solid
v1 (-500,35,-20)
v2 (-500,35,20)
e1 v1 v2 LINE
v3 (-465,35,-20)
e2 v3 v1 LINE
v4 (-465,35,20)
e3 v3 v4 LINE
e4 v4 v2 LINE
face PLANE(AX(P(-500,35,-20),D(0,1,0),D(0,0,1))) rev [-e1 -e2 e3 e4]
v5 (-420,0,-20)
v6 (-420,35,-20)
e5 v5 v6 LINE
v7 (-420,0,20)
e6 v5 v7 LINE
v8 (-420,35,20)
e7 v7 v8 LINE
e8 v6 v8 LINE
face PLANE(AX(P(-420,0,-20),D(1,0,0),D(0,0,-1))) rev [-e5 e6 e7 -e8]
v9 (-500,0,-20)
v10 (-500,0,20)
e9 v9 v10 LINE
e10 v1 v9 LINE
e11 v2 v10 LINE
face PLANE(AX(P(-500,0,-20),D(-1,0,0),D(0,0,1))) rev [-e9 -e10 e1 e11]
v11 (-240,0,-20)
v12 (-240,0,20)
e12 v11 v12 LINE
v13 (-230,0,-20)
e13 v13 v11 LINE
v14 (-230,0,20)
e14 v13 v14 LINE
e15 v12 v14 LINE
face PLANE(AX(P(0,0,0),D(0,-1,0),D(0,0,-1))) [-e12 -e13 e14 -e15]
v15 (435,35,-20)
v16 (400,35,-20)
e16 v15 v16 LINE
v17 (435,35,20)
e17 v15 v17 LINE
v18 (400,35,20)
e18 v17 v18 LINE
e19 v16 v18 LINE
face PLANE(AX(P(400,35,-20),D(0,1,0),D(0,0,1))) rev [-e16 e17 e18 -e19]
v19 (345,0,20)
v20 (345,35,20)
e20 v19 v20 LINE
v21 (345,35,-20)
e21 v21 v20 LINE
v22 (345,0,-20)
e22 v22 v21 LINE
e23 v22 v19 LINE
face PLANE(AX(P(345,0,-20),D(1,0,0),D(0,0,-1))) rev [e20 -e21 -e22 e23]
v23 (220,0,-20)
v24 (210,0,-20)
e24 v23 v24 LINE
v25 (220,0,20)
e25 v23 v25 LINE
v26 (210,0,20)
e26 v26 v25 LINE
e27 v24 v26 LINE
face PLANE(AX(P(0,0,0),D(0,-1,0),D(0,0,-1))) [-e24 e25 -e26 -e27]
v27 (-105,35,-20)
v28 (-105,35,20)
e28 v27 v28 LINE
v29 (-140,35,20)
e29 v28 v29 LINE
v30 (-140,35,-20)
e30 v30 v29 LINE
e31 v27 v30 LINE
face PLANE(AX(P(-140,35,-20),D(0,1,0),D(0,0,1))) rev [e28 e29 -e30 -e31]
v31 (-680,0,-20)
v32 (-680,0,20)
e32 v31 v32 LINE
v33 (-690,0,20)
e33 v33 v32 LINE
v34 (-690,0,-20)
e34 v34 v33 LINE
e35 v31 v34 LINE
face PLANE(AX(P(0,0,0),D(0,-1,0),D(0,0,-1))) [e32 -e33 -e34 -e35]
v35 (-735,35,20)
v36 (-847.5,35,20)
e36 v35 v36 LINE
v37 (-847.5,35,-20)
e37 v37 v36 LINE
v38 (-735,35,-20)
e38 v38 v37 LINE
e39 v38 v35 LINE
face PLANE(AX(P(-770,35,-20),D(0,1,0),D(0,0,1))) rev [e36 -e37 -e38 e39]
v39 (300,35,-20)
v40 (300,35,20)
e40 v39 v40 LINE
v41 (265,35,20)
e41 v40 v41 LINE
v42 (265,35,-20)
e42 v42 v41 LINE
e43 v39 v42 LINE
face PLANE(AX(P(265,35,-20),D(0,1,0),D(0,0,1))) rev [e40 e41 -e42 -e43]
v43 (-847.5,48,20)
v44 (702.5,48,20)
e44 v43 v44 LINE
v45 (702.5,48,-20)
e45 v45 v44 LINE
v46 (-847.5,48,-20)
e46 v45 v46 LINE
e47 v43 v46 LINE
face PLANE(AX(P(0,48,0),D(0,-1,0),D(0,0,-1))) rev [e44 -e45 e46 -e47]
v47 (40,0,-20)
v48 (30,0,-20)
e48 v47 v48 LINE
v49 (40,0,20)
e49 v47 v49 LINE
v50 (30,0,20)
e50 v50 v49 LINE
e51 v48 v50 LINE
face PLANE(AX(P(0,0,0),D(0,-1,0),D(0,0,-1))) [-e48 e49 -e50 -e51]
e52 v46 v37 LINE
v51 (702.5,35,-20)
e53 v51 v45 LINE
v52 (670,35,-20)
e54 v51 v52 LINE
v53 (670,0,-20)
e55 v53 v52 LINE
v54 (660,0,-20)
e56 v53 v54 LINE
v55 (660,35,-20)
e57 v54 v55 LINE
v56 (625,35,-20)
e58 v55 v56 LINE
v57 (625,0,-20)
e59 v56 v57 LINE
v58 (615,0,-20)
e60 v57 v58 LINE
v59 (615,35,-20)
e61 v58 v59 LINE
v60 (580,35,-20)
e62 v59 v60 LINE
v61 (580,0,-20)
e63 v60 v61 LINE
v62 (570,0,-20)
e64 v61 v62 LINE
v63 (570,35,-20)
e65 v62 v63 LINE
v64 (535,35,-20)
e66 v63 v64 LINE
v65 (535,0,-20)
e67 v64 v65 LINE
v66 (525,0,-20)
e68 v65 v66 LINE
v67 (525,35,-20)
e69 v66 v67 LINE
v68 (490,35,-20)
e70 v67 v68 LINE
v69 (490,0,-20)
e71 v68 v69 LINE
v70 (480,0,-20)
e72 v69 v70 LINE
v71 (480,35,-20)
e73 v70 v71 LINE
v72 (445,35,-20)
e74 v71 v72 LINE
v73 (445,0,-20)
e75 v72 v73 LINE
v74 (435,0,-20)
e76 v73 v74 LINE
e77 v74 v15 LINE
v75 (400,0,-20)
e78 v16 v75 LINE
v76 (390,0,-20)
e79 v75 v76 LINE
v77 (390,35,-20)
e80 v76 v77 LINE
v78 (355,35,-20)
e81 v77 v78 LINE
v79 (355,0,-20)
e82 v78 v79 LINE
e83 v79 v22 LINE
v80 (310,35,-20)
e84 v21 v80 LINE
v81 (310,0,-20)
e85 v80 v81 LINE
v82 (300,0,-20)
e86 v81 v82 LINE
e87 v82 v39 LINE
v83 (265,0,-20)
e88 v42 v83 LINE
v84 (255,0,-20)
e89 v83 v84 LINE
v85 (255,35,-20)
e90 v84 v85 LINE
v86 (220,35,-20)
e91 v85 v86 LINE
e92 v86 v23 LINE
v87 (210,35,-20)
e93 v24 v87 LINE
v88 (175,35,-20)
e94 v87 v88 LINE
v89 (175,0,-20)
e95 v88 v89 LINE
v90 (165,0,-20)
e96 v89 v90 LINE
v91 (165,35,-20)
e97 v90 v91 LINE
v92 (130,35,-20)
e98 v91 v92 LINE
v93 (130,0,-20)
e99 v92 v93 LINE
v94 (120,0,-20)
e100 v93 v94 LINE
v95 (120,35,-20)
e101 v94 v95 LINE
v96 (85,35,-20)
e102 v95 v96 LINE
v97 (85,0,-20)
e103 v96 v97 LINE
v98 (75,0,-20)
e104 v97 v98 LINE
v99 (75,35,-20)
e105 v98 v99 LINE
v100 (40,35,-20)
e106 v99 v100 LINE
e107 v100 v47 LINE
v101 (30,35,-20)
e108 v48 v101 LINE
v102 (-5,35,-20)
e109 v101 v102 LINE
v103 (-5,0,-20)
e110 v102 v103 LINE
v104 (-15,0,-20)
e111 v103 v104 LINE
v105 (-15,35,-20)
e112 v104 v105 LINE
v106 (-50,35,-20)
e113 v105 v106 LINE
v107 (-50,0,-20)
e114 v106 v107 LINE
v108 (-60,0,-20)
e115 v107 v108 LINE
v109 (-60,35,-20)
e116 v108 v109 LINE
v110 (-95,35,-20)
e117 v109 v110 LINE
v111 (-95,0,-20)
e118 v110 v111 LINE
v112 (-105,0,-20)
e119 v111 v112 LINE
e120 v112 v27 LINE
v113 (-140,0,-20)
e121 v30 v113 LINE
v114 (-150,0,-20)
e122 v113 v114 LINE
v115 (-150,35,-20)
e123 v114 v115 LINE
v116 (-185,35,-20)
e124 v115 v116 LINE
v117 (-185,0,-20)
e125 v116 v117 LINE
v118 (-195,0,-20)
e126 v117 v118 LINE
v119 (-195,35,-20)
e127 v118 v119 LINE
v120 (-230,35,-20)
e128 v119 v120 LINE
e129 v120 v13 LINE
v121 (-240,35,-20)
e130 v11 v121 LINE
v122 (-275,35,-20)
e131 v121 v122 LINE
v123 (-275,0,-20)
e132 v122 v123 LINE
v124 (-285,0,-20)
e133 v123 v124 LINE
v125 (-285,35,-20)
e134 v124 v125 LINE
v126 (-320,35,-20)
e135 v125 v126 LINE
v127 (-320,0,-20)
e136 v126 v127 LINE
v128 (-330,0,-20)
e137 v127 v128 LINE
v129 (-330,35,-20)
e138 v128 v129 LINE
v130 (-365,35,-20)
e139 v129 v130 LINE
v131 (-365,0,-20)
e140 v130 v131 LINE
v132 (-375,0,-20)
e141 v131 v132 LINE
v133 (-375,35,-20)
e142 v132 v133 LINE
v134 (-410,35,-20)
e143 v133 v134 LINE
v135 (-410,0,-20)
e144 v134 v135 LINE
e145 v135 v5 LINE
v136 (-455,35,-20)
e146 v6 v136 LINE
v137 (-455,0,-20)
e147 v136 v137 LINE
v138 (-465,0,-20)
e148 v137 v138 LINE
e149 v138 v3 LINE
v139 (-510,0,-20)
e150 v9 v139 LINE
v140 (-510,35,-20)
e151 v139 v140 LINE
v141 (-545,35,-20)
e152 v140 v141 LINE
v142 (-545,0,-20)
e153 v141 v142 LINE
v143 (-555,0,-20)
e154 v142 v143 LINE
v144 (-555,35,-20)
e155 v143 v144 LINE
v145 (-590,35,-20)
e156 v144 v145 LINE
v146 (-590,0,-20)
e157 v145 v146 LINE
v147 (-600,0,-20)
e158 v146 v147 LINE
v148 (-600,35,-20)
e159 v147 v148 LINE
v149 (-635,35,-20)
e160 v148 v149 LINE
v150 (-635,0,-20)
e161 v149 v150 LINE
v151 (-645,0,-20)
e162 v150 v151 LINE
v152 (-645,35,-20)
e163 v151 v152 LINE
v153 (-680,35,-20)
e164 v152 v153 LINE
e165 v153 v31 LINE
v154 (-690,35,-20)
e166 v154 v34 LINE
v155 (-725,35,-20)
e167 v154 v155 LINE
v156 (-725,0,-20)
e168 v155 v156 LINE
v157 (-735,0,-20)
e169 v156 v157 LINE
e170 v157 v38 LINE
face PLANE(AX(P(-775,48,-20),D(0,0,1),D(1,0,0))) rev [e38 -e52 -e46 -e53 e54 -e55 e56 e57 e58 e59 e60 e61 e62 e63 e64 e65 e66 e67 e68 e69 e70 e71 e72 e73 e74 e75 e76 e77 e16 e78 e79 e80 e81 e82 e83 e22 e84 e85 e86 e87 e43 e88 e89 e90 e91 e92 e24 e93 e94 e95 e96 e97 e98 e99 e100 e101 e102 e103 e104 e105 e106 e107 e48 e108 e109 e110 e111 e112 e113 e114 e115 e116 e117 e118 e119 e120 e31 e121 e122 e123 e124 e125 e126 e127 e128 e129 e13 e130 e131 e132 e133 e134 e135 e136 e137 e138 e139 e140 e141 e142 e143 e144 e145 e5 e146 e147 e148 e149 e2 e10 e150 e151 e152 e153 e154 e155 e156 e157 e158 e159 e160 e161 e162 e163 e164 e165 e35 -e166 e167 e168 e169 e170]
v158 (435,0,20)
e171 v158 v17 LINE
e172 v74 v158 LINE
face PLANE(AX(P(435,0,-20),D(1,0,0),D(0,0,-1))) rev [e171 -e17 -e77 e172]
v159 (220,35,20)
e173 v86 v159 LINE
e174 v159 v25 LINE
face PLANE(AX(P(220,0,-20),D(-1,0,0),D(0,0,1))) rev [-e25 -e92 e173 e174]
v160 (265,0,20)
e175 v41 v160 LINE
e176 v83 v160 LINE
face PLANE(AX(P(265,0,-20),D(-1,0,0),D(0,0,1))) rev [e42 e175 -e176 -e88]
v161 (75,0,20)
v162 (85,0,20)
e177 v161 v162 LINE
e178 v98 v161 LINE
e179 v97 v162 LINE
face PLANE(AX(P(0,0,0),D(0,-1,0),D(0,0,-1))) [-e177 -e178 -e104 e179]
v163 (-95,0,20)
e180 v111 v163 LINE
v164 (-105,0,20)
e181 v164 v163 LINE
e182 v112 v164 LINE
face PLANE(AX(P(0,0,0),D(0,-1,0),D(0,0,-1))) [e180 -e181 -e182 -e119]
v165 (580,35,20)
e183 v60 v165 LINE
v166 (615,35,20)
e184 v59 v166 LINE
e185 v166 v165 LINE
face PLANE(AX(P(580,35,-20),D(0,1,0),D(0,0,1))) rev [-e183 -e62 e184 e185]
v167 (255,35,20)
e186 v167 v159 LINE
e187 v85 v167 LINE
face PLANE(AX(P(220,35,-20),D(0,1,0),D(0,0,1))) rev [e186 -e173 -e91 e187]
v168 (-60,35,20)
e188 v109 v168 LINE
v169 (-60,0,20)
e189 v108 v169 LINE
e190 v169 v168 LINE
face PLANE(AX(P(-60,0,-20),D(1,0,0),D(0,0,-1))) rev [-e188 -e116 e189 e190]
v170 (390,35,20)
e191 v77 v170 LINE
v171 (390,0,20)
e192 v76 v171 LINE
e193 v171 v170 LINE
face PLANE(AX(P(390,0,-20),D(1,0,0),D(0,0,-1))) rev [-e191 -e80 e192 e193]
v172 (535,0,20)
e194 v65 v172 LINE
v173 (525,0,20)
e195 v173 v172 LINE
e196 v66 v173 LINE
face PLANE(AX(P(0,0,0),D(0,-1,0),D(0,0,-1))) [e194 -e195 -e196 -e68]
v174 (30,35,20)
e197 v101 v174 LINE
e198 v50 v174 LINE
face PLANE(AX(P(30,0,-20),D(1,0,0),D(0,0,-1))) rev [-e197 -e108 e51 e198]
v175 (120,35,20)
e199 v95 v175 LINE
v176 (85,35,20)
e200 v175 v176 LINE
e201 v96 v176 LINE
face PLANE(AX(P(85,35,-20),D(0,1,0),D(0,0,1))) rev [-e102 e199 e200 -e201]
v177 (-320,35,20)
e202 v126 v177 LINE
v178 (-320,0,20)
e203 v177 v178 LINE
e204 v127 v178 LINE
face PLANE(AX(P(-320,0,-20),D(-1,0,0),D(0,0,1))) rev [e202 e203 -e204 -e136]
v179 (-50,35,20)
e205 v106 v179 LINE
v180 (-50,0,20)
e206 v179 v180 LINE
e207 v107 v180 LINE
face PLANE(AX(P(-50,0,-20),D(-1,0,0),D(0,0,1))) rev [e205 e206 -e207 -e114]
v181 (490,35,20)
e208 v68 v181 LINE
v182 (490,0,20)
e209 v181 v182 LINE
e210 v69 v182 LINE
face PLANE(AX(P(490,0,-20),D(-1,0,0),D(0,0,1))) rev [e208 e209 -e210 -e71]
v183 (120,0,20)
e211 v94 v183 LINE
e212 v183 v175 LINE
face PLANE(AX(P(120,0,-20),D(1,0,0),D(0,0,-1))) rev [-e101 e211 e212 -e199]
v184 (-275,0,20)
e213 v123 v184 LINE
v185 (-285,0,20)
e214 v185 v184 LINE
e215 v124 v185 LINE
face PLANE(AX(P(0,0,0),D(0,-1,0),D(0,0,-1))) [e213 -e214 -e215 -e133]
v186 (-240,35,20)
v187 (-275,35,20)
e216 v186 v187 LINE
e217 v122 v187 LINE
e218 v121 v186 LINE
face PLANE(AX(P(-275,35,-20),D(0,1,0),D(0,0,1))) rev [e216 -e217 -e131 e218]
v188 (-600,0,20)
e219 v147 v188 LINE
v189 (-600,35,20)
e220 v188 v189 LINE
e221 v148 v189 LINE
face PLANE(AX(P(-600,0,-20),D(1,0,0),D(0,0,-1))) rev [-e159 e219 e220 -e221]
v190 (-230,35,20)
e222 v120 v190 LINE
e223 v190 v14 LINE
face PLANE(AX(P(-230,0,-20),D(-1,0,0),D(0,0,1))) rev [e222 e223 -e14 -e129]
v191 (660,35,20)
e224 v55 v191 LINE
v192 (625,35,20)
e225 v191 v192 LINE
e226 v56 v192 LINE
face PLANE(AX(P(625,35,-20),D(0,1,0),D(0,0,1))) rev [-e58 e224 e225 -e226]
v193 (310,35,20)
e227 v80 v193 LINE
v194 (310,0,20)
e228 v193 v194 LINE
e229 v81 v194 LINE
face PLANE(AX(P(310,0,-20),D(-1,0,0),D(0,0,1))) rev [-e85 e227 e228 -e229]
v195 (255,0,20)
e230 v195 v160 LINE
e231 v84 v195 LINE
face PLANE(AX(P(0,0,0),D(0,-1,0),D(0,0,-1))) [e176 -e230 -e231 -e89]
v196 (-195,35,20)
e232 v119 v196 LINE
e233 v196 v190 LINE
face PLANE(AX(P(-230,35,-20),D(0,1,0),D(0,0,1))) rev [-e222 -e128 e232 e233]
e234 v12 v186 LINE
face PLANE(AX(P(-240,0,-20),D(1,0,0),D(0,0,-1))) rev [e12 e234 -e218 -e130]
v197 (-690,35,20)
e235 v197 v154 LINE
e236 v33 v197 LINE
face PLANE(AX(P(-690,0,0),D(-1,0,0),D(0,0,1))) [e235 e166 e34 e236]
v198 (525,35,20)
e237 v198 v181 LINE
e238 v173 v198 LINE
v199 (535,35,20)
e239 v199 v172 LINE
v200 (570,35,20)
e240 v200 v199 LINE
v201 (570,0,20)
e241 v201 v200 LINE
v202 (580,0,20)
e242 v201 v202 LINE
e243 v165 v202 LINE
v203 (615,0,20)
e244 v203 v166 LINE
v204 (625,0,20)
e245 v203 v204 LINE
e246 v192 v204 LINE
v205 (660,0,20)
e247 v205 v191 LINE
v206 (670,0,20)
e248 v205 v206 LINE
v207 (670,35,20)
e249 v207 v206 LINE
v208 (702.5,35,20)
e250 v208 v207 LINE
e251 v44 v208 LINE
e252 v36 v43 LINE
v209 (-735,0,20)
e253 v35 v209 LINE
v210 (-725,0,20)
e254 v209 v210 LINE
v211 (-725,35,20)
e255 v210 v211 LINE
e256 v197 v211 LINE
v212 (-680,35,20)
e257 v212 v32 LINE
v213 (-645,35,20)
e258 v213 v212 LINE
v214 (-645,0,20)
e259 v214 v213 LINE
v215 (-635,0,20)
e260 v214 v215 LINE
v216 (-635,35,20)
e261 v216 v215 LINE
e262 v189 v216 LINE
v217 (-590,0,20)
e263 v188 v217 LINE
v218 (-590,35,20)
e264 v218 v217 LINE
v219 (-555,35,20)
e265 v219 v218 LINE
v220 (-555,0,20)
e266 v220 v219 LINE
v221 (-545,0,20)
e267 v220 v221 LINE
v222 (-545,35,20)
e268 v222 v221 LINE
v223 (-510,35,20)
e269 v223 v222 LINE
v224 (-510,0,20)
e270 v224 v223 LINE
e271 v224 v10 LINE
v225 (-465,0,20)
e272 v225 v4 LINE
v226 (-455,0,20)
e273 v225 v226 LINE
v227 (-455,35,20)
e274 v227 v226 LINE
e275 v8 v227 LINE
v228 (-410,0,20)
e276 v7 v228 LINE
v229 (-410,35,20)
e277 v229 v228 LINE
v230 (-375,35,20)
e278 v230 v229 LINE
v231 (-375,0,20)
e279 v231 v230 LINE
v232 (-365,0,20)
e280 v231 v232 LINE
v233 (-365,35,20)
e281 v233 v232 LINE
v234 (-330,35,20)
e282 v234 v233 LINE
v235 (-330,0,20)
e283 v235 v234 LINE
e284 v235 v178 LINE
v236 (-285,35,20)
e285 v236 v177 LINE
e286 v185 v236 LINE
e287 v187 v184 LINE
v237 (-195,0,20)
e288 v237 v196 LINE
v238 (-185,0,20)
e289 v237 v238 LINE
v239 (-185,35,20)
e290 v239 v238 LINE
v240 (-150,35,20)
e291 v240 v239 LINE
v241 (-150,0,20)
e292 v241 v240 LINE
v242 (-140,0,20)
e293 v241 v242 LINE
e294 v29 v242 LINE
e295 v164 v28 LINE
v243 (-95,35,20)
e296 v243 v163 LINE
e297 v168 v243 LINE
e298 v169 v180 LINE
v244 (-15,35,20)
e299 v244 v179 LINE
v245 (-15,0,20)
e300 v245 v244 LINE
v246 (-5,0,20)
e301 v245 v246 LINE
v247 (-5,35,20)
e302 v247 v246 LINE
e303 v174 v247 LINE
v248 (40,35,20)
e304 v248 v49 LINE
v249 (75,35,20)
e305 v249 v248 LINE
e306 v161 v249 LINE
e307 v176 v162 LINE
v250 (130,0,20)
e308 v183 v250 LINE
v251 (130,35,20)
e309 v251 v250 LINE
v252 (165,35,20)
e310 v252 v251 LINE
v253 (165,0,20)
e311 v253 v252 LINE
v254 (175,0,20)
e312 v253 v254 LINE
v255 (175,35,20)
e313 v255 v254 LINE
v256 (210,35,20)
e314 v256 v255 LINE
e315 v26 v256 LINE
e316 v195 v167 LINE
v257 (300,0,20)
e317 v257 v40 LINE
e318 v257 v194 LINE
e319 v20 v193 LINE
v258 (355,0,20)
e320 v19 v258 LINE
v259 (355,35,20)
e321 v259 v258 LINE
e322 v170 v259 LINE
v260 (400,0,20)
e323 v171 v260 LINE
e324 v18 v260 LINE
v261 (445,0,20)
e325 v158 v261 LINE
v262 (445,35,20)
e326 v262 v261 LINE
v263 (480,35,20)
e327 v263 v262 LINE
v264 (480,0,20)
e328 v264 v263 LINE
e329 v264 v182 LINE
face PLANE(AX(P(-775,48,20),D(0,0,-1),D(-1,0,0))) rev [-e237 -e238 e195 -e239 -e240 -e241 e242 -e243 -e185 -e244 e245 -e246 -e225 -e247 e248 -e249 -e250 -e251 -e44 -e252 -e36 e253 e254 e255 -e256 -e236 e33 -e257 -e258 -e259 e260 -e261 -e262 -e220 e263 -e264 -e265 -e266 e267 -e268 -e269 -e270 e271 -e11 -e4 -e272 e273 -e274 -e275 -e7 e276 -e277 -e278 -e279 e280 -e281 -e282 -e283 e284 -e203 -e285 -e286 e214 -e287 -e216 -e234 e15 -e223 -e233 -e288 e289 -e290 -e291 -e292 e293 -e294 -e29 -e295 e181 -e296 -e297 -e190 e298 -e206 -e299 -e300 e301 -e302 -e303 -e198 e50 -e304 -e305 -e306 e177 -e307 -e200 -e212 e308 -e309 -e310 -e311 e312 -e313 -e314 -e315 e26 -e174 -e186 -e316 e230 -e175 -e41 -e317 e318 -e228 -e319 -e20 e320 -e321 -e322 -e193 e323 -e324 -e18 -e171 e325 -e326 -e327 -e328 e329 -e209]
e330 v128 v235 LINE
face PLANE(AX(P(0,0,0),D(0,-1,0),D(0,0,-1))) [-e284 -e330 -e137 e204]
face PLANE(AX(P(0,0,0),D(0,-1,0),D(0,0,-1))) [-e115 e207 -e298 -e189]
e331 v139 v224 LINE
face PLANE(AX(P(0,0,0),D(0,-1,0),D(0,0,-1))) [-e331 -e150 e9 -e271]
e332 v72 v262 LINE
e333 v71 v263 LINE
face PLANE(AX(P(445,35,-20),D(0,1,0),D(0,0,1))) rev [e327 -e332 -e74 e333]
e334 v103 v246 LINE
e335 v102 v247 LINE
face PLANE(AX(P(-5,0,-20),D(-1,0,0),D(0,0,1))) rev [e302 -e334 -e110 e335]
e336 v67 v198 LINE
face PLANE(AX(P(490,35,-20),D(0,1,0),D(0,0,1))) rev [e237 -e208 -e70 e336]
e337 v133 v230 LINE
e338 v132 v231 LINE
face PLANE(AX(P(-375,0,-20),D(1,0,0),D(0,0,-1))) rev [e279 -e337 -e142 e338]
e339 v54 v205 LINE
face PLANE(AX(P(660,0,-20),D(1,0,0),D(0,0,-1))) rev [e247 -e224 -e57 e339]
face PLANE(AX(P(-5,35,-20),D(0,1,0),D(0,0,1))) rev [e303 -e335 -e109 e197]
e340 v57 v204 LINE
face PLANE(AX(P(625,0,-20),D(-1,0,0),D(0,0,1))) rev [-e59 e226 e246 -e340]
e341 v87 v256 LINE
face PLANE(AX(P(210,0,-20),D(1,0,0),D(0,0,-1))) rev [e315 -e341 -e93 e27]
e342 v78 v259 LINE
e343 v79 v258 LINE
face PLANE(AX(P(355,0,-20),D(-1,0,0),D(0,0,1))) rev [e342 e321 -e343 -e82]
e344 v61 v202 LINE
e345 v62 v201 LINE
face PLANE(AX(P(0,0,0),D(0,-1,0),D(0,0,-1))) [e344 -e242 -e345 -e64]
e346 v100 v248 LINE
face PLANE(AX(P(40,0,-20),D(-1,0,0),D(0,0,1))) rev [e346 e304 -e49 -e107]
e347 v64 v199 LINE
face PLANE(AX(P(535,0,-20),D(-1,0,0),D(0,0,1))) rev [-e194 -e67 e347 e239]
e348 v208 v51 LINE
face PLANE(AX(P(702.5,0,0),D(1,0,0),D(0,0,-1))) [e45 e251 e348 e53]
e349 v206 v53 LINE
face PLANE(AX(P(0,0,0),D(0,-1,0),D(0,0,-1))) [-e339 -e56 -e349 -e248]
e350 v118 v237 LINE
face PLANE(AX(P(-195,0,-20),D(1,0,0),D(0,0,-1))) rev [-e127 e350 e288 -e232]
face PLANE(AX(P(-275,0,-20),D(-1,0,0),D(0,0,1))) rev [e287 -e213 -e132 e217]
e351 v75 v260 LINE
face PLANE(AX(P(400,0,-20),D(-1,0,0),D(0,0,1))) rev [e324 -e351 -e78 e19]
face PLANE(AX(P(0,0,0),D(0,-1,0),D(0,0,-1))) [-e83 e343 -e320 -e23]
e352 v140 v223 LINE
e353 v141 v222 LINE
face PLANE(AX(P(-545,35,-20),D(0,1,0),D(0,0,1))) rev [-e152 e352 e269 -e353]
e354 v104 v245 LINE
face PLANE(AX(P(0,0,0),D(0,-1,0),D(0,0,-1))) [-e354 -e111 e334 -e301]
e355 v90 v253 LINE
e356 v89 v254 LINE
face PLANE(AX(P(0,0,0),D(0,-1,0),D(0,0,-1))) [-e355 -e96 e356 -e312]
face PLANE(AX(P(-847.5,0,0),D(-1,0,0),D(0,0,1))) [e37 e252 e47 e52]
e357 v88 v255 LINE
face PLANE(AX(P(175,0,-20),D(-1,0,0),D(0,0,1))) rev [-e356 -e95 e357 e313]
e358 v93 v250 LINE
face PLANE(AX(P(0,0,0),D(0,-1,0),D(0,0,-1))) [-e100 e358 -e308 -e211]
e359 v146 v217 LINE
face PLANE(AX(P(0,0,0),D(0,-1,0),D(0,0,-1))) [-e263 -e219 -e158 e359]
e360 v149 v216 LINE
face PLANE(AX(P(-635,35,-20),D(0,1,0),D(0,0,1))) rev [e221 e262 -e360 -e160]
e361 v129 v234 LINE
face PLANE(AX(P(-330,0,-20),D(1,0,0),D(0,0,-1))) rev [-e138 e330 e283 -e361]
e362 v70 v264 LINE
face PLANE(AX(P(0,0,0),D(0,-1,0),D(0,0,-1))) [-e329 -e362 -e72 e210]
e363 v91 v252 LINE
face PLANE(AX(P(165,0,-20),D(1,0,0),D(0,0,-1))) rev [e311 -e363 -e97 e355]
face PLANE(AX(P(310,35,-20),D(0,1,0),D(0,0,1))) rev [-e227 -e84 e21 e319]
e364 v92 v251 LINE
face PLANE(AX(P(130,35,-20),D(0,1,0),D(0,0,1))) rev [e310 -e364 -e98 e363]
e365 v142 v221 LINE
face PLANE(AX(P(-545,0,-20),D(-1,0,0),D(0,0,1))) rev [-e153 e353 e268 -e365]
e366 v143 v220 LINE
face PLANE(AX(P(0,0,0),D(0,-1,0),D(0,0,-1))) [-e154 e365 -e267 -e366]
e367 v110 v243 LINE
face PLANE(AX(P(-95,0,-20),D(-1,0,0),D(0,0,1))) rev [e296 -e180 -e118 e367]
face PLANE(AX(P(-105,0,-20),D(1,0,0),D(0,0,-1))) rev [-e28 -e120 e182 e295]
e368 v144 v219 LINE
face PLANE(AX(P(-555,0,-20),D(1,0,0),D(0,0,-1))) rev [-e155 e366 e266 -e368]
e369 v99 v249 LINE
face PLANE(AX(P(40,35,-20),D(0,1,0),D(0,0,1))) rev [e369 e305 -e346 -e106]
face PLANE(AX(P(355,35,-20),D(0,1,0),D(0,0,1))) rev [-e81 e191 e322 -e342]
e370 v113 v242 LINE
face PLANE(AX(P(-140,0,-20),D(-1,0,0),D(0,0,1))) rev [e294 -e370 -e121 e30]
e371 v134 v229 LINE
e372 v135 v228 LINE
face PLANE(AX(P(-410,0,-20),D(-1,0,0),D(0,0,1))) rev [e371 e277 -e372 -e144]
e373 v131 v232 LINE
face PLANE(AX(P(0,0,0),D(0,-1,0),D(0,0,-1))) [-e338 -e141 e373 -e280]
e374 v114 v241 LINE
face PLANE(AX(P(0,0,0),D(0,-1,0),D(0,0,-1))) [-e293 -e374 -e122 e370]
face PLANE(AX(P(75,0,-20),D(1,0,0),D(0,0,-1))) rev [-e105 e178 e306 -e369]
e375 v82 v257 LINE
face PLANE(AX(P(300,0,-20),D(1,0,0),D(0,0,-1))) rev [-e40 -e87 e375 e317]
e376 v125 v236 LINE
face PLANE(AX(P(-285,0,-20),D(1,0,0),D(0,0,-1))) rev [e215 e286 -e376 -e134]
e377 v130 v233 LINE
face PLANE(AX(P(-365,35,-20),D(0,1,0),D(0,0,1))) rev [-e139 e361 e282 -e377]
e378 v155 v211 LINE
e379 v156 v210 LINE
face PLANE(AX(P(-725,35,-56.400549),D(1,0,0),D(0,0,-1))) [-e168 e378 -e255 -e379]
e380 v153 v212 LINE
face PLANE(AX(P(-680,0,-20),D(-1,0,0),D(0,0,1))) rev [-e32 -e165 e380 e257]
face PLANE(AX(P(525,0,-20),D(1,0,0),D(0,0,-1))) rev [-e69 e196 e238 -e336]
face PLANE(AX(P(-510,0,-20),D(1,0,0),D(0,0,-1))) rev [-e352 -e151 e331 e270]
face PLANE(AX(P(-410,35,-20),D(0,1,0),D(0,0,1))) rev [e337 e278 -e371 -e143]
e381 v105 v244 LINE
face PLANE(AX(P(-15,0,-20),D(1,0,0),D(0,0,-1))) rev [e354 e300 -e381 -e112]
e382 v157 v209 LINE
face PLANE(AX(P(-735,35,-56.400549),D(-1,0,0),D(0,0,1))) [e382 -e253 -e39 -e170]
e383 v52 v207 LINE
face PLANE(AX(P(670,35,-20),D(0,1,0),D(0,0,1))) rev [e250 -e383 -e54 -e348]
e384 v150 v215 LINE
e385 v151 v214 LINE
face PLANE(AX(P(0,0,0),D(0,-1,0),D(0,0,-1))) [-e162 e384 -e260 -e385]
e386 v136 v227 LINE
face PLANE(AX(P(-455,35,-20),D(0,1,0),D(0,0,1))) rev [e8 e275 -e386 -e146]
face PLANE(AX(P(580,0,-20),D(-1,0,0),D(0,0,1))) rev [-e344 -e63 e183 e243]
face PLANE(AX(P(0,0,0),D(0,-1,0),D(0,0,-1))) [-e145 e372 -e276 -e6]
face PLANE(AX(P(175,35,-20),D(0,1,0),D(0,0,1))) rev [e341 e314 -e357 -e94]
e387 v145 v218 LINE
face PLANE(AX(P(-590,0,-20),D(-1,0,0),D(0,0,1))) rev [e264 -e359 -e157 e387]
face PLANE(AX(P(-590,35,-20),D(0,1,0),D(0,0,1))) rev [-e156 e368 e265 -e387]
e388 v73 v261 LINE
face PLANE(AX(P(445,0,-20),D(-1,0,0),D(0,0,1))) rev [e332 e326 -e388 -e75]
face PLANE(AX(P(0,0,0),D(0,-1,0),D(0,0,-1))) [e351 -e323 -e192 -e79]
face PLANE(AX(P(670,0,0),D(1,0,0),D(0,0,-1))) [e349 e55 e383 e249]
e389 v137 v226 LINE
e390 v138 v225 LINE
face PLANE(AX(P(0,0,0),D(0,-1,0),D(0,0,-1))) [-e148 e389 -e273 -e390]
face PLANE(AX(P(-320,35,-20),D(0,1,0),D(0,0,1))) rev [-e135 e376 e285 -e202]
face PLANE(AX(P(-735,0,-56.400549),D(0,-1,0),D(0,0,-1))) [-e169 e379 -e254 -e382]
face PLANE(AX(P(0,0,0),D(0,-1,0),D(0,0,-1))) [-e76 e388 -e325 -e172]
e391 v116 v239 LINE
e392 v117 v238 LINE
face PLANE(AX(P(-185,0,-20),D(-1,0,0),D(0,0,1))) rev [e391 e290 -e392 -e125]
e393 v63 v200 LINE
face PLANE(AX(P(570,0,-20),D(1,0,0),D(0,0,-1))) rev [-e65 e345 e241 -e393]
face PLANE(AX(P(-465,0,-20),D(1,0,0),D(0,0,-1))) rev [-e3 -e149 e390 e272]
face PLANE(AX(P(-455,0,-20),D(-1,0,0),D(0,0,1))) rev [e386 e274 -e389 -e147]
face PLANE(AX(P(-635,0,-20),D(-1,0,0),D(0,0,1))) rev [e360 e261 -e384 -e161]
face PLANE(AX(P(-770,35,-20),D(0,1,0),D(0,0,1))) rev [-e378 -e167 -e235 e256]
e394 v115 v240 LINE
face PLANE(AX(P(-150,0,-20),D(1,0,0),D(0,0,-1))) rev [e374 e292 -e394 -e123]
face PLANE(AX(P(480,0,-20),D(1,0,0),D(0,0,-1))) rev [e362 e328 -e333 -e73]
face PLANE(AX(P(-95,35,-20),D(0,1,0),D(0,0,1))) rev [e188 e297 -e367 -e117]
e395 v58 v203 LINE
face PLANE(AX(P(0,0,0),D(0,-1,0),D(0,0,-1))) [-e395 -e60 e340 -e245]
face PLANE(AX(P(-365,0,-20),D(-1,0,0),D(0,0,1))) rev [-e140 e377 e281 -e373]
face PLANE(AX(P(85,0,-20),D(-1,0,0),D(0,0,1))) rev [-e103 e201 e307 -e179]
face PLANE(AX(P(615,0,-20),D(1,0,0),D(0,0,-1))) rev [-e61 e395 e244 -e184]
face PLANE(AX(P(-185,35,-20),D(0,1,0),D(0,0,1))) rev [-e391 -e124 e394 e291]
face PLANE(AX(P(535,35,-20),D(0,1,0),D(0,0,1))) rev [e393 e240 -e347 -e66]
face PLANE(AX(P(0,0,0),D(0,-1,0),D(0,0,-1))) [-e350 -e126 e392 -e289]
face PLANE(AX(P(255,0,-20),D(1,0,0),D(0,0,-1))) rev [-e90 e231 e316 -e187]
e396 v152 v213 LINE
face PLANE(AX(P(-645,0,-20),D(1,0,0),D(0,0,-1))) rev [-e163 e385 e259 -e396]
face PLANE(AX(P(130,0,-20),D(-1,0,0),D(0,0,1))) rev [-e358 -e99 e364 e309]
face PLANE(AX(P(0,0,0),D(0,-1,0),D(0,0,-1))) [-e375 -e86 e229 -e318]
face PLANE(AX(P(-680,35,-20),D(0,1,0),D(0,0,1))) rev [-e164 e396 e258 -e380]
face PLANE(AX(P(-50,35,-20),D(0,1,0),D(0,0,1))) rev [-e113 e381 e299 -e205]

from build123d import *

# Parameters (mm, degrees)
SKETCH_1_W          = 1550
SKETCH_1_H          = 40
EXTRUDE_1_DEPTH     = 48
SKETCH_2_W          = 35
SKETCH_2_H          = 35
CUT_EXTRUDE_1_DEPTH = 778.514630087
SKETCH_6_W          = 35
SKETCH_6_H          = 35
CUT_EXTRUDE_5_DEPTH = 778.514630087
SKETCH_7_W          = 110
SKETCH_7_H          = 61.445783933
SKETCH_7_W_2        = 90
SKETCH_7_H_2        = 84.634966513
CUT_EXTRUDE_6_DEPTH = 778.514630087
SKETCH_8_W          = 40
SKETCH_8_H          = 13
EXTRUDE_2_DEPTH     = 10
SKETCH_9_W          = 40
SKETCH_9_H          = 13
CUT_EXTRUDE_7_DEPTH = 10
SKETCH_10_W         = 40
SKETCH_10_H         = 35
EXTRUDE_3_DEPTH     = 5
SKETCH_11_W         = 40
SKETCH_11_H         = 35
EXTRUDE_4_DEPTH     = 5
MOVE_FACE_1_BY      = 22.5
MOVE_FACE_1_2_BY    = 22.5
SKETCH_12_W         = 10
SKETCH_12_H         = 35
EXTRUDE_5_DEPTH     = 40
MOVE_FACE_2_BY      = 40
MOVE_FACE_2_2_BY    = 40


with BuildPart() as part:
    # 草图1 → 凸台-拉伸1 (new body)
    with BuildSketch(Plane(origin=(0, 0, 0), x_dir=(1, 0, 0), z_dir=(0, 1, 0))):
        Rectangle(SKETCH_1_W, SKETCH_1_H)
    extrude(amount=EXTRUDE_1_DEPTH)

    # 草图2 → 切除-拉伸1 (cut, through all)
    with BuildSketch(Plane.XY.offset(20)):
        with Locations((-752.5, 17.5)):
            Rectangle(SKETCH_2_W, SKETCH_2_H)
        with Locations((-707.5, 17.5)):
            Rectangle(SKETCH_2_W, SKETCH_2_H)
        with Locations((-662.5, 17.5)):
            Rectangle(SKETCH_2_W, SKETCH_2_H)
        with Locations((-617.5, 17.5)):
            Rectangle(SKETCH_2_W, SKETCH_2_H)
        with Locations((-572.5, 17.5)):
            Rectangle(SKETCH_2_W, SKETCH_2_H)
        with Locations((-527.5, 17.5)):
            Rectangle(SKETCH_2_W, SKETCH_2_H)
        with Locations((-482.5, 17.5)):
            Rectangle(SKETCH_2_W, SKETCH_2_H)
        with Locations((-437.5, 17.5)):
            Rectangle(SKETCH_2_W, SKETCH_2_H)
        with Locations((-392.5, 17.5)):
            Rectangle(SKETCH_2_W, SKETCH_2_H)
        with Locations((-347.5, 17.5)):
            Rectangle(SKETCH_2_W, SKETCH_2_H)
        with Locations((-302.5, 17.5)):
            Rectangle(SKETCH_2_W, SKETCH_2_H)
        with Locations((-257.5, 17.5)):
            Rectangle(SKETCH_2_W, SKETCH_2_H)
    extrude(amount=-CUT_EXTRUDE_1_DEPTH, mode=Mode.SUBTRACT)

    # 草图6 → 切除-拉伸5 (cut, through all)
    with BuildSketch(Plane.XY.offset(20)):
        with Locations((-212.5, 17.5)):
            Rectangle(SKETCH_6_W, SKETCH_6_H)
        with Locations((-77.5, 17.5)):
            Rectangle(SKETCH_6_W, SKETCH_6_H)
        with Locations((-167.5, 17.5)):
            Rectangle(SKETCH_6_W, SKETCH_6_H)
        with Locations((-122.5, 17.5)):
            Rectangle(SKETCH_6_W, SKETCH_6_H)
        with Locations((-32.5, 17.5)):
            Rectangle(SKETCH_6_W, SKETCH_6_H)
        with Locations((12.5, 17.5)):
            Rectangle(SKETCH_6_W, SKETCH_6_H)
        with Locations((57.5, 17.5)):
            Rectangle(SKETCH_6_W, SKETCH_6_H)
        with Locations((102.5, 17.5)):
            Rectangle(SKETCH_6_W, SKETCH_6_H)
        with Locations((147.5, 17.5)):
            Rectangle(SKETCH_6_W, SKETCH_6_H)
        with Locations((192.5, 17.5)):
            Rectangle(SKETCH_6_W, SKETCH_6_H)
        with Locations((237.5, 17.5)):
            Rectangle(SKETCH_6_W, SKETCH_6_H)
        with Locations((282.5, 17.5)):
            Rectangle(SKETCH_6_W, SKETCH_6_H)
        with Locations((327.5, 17.5)):
            Rectangle(SKETCH_6_W, SKETCH_6_H)
        with Locations((372.5, 17.5)):
            Rectangle(SKETCH_6_W, SKETCH_6_H)
        with Locations((417.5, 17.5)):
            Rectangle(SKETCH_6_W, SKETCH_6_H)
        with Locations((462.5, 17.5)):
            Rectangle(SKETCH_6_W, SKETCH_6_H)
        with Locations((507.5, 17.5)):
            Rectangle(SKETCH_6_W, SKETCH_6_H)
        with Locations((552.5, 17.5)):
            Rectangle(SKETCH_6_W, SKETCH_6_H)
        with Locations((597.5, 17.5)):
            Rectangle(SKETCH_6_W, SKETCH_6_H)
        with Locations((642.5, 17.5)):
            Rectangle(SKETCH_6_W, SKETCH_6_H)
        with Locations((687.5, 17.5)):
            Rectangle(SKETCH_6_W, SKETCH_6_H)
        with Locations((732.5, 17.5)):
            Rectangle(SKETCH_6_W, SKETCH_6_H)
    extrude(amount=-CUT_EXTRUDE_5_DEPTH, mode=Mode.SUBTRACT)

    # 草图7 → 切除-拉伸6 (cut, through all)
    with BuildSketch(Plane(origin=(0, 0, -20), x_dir=(-1, 0, 0), z_dir=(0, 0, -1))):
        with Locations((-720, 4.277108033)):
            Rectangle(SKETCH_7_W, SKETCH_7_H)
        with Locations((730, -7.317483257)):
            Rectangle(SKETCH_7_W_2, SKETCH_7_H_2)
    extrude(amount=-CUT_EXTRUDE_6_DEPTH, mode=Mode.SUBTRACT)

    # 草图8 → 凸台-拉伸2 (add)
    with BuildSketch(Plane.ZY.offset(775)):
        with Locations((0, 41.5)):
            Rectangle(SKETCH_8_W, SKETCH_8_H)
    extrude(amount=EXTRUDE_2_DEPTH)

    # 草图9 → 切除-拉伸7 (cut)
    with BuildSketch(Plane(origin=(775, 0, 0), x_dir=(0, 0, -1), z_dir=(1, 0, 0))):
        with Locations((0, 41.5)):
            Rectangle(SKETCH_9_W, SKETCH_9_H)
    extrude(amount=-CUT_EXTRUDE_7_DEPTH, mode=Mode.SUBTRACT)

    # 草图10 → 凸台-拉伸3 (add)
    with BuildSketch(Plane(origin=(665, 0, 0), x_dir=(0, 0, -1), z_dir=(1, 0, 0))):
        with Locations((0, 17.5)):
            Rectangle(SKETCH_10_W, SKETCH_10_H)
    extrude(amount=EXTRUDE_3_DEPTH)

    # 草图11 → 凸台-拉伸4 (add)
    with BuildSketch(Plane.ZY.offset(685)):
        with Locations((0, 17.5)):
            Rectangle(SKETCH_11_W, SKETCH_11_H)
    extrude(amount=EXTRUDE_4_DEPTH)

    # Move Face 1: a face moved outward by 22.5
    extrude(part.faces().sort_by_distance((-785, 41.5, 0))[0], amount=MOVE_FACE_1_BY, dir=(-1, 0, 0))

    # Move Face 1 2: a face moved inward by 22.5
    extrude(part.faces().sort_by_distance((765, 41.5, 0))[0], amount=MOVE_FACE_1_2_BY, dir=(-1, 0, 0), mode=Mode.SUBTRACT)

    # 草图12 → 凸台-拉伸5 (add)
    with BuildSketch(Plane.XY.offset(20)):
        with Locations((-730, 17.5)):
            Rectangle(SKETCH_12_W, SKETCH_12_H)
    extrude(amount=-EXTRUDE_5_DEPTH)

    # Move Face 2: a face moved outward by 40.0
    extrude(part.faces().sort_by_distance((-807.5, 41.5, 0))[0], amount=MOVE_FACE_2_BY, dir=(-1, 0, 0))

    # Move Face 2 2: a face moved inward by 40.0
    extrude(part.faces().sort_by_distance((742.5, 41.5, 0))[0], amount=MOVE_FACE_2_2_BY, dir=(-1, 0, 0), mode=Mode.SUBTRACT)


solid = part.part
